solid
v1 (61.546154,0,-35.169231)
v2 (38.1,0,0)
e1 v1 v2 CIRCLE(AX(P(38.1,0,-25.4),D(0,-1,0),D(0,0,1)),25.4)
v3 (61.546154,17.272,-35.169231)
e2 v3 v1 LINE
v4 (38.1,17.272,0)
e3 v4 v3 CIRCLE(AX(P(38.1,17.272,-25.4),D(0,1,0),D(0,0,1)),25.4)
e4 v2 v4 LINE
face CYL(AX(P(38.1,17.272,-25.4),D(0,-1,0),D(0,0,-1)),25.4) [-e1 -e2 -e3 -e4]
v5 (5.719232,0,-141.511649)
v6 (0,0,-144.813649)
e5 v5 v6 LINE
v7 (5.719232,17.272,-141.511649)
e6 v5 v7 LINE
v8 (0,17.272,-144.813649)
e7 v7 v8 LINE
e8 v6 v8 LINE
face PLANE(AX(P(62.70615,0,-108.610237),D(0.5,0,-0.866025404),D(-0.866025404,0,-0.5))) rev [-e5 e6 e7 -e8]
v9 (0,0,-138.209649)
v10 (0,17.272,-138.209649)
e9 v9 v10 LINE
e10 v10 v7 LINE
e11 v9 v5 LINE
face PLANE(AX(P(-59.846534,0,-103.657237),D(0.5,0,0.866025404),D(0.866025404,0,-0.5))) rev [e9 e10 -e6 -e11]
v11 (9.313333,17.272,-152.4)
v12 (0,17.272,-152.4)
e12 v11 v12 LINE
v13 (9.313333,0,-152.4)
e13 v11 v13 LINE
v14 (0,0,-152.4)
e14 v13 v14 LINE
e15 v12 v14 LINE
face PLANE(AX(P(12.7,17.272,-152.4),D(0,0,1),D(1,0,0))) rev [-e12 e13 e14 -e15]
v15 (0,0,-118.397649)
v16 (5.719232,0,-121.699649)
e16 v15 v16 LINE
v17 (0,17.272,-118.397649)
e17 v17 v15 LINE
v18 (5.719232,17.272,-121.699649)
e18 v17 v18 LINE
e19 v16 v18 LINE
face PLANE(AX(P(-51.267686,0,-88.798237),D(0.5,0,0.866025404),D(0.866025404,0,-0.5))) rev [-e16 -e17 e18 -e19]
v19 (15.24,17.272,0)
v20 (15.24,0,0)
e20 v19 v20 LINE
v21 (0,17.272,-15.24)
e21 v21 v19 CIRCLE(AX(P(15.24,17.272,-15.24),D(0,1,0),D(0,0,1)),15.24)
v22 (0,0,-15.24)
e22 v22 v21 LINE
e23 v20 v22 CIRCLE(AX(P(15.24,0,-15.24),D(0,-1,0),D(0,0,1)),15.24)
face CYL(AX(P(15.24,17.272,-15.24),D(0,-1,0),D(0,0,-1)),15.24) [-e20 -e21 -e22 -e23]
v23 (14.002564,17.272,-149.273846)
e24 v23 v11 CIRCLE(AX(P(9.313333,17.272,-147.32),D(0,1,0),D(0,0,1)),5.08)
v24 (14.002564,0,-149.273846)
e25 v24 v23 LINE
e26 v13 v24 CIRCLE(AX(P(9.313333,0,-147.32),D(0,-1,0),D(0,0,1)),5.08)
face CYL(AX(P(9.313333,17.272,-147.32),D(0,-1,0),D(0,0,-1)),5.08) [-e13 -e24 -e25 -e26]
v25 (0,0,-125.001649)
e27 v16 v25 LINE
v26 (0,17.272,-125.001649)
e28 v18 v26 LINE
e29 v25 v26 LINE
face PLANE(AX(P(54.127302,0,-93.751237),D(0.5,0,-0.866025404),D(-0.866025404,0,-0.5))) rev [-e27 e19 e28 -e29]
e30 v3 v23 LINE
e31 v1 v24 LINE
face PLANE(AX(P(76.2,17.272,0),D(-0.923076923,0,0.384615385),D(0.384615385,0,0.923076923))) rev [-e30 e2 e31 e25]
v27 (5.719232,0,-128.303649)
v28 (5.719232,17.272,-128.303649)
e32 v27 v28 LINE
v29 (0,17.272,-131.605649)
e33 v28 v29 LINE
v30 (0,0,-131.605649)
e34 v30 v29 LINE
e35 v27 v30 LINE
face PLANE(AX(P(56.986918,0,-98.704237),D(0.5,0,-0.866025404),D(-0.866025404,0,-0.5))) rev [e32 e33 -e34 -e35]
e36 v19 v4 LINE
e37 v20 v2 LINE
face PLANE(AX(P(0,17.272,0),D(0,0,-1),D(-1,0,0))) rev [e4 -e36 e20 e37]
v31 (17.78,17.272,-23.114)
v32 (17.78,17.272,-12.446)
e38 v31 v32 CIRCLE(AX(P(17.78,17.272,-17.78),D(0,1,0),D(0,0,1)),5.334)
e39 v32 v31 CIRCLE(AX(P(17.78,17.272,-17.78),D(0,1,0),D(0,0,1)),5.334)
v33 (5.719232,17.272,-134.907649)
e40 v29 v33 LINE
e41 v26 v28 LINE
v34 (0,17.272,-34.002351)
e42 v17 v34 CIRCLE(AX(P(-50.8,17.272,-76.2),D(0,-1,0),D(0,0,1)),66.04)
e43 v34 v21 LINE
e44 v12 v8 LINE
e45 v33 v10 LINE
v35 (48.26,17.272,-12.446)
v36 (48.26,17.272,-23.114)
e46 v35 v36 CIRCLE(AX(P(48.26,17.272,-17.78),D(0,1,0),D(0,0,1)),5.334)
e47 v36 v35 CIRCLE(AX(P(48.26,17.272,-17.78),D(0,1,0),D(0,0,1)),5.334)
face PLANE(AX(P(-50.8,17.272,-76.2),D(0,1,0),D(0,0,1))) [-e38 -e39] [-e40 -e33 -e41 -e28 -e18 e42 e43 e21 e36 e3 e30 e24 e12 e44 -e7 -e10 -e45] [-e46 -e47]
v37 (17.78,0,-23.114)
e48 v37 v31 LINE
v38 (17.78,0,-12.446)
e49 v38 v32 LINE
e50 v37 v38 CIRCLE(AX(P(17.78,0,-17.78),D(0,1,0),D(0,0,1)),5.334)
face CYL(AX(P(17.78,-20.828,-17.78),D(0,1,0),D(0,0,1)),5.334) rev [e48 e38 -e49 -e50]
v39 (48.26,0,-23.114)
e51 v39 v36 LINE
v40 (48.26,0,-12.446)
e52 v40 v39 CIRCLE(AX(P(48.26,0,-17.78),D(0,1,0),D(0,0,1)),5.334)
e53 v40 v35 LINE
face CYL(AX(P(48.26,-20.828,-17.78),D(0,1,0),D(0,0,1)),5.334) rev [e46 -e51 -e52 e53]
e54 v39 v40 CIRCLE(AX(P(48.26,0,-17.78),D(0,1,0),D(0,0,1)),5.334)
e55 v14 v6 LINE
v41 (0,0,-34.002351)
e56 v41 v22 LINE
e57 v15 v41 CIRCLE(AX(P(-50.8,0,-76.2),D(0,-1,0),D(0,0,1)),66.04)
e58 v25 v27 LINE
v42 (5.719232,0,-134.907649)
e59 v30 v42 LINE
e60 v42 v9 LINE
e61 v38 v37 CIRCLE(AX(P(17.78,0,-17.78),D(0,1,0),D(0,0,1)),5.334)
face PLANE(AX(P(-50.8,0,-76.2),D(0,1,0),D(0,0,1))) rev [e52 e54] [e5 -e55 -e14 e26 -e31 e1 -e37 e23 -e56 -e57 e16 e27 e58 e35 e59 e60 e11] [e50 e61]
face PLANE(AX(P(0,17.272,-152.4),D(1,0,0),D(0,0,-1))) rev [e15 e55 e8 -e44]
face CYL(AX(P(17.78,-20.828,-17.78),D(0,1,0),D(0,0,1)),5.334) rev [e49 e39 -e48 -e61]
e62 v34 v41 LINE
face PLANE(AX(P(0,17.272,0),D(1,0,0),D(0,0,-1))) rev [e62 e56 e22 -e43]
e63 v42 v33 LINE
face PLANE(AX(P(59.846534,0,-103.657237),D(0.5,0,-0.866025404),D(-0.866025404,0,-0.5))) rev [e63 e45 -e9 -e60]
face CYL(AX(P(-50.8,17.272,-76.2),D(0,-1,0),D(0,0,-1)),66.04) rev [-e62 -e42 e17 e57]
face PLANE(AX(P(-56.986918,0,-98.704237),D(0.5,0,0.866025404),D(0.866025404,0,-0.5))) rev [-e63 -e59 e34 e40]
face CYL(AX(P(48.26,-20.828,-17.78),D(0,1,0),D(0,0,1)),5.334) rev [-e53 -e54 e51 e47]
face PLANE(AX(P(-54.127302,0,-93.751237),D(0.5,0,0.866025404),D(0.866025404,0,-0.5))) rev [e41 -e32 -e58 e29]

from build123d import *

# Parameters (mm, degrees)
BOSS_EXTRUDE1_DEPTH = 8.636
SKETCH3_R           = 2.667
CUT_EXTRUDE1_DEPTH  = 19.05
FILLET1_R           = 12.7
FILLET2_R           = 2.54
FILLET3_R           = 7.62
CUT_EXTRUDE2_DEPTH  = 84.000499974
SCALE1_SCALE        = 2


with BuildPart() as part:
    # Sketch1 → Boss-Extrude1 (new body)
    with BuildSketch(Plane(origin=(0, 0, 0), x_dir=(1, 0, 0), z_dir=(0, 1, 0))):
        with BuildLine():
            Line((0, 0), (38.1, 0))
            Line((38.1, 0), (6.35, 76.2))
            Line((6.35, 76.2), (0, 76.2))
            Line((0, 76.2), (0, 59.198824612))
            ThreePointArc((0, 59.198824612), (7.62, 38.1), (0, 17.001175388))
            Line((0, 17.001175388), (0, 0))
        make_face()
    extrude(amount=BOSS_EXTRUDE1_DEPTH)

    # Sketch3 → Cut-Extrude1 (cut)
    with BuildSketch(Plane(origin=(0, 8.636, 0), x_dir=(1, 0, 0), z_dir=(0, 1, 0))):
        with Locations(Location((8.89, 8.89, 0), (0, 0, 270))):
            Circle(SKETCH3_R)
        with Locations(Location((24.13, 8.89, 0), (0, 0, 270))):
            Circle(SKETCH3_R)
    extrude(amount=-CUT_EXTRUDE1_DEPTH, mode=Mode.SUBTRACT)

    # Fillet1
    fillet1_edges = [part.edges().sort_by_distance(p)[0] for p in [
        (38.1, 4.318, 0),
    ]]
    fillet(fillet1_edges, radius=FILLET1_R)

    # Fillet2
    fillet2_edges = [part.edges().sort_by_distance(p)[0] for p in [
        (6.35, 4.318, -76.2),
    ]]
    fillet(fillet2_edges, radius=FILLET2_R)

    # Fillet3
    fillet3_edges = [part.edges().sort_by_distance(p)[0] for p in [
        (0, 4.318, 0),
    ]]
    fillet(fillet3_edges, radius=FILLET3_R)

    # Sketch4 → Cut-Extrude2 (cut, through all)
    with BuildSketch(Plane(origin=(0, 8.636, 0), x_dir=(1, 0, 0), z_dir=(0, 1, 0))):
        Polygon((0, 62.500824612), (0, 59.198824612), (2.859615883, 60.849824612), align=None)
        Polygon((0, 65.802824612), (0, 62.500824612), (2.859615883, 64.151824612), align=None)
        Polygon((0, 69.104824612), (0, 65.802824612), (2.859615883, 67.453824612), align=None)
        Polygon((0, 72.406824612), (0, 69.104824612), (2.859615883, 70.755824612), align=None)
    extrude(amount=-CUT_EXTRUDE2_DEPTH, mode=Mode.SUBTRACT)


with BuildPart() as part_1:
    # Scale1: scaled about (0, 0, 0)
    add(part.part.scale(SCALE1_SCALE))


solid = part_1.part
